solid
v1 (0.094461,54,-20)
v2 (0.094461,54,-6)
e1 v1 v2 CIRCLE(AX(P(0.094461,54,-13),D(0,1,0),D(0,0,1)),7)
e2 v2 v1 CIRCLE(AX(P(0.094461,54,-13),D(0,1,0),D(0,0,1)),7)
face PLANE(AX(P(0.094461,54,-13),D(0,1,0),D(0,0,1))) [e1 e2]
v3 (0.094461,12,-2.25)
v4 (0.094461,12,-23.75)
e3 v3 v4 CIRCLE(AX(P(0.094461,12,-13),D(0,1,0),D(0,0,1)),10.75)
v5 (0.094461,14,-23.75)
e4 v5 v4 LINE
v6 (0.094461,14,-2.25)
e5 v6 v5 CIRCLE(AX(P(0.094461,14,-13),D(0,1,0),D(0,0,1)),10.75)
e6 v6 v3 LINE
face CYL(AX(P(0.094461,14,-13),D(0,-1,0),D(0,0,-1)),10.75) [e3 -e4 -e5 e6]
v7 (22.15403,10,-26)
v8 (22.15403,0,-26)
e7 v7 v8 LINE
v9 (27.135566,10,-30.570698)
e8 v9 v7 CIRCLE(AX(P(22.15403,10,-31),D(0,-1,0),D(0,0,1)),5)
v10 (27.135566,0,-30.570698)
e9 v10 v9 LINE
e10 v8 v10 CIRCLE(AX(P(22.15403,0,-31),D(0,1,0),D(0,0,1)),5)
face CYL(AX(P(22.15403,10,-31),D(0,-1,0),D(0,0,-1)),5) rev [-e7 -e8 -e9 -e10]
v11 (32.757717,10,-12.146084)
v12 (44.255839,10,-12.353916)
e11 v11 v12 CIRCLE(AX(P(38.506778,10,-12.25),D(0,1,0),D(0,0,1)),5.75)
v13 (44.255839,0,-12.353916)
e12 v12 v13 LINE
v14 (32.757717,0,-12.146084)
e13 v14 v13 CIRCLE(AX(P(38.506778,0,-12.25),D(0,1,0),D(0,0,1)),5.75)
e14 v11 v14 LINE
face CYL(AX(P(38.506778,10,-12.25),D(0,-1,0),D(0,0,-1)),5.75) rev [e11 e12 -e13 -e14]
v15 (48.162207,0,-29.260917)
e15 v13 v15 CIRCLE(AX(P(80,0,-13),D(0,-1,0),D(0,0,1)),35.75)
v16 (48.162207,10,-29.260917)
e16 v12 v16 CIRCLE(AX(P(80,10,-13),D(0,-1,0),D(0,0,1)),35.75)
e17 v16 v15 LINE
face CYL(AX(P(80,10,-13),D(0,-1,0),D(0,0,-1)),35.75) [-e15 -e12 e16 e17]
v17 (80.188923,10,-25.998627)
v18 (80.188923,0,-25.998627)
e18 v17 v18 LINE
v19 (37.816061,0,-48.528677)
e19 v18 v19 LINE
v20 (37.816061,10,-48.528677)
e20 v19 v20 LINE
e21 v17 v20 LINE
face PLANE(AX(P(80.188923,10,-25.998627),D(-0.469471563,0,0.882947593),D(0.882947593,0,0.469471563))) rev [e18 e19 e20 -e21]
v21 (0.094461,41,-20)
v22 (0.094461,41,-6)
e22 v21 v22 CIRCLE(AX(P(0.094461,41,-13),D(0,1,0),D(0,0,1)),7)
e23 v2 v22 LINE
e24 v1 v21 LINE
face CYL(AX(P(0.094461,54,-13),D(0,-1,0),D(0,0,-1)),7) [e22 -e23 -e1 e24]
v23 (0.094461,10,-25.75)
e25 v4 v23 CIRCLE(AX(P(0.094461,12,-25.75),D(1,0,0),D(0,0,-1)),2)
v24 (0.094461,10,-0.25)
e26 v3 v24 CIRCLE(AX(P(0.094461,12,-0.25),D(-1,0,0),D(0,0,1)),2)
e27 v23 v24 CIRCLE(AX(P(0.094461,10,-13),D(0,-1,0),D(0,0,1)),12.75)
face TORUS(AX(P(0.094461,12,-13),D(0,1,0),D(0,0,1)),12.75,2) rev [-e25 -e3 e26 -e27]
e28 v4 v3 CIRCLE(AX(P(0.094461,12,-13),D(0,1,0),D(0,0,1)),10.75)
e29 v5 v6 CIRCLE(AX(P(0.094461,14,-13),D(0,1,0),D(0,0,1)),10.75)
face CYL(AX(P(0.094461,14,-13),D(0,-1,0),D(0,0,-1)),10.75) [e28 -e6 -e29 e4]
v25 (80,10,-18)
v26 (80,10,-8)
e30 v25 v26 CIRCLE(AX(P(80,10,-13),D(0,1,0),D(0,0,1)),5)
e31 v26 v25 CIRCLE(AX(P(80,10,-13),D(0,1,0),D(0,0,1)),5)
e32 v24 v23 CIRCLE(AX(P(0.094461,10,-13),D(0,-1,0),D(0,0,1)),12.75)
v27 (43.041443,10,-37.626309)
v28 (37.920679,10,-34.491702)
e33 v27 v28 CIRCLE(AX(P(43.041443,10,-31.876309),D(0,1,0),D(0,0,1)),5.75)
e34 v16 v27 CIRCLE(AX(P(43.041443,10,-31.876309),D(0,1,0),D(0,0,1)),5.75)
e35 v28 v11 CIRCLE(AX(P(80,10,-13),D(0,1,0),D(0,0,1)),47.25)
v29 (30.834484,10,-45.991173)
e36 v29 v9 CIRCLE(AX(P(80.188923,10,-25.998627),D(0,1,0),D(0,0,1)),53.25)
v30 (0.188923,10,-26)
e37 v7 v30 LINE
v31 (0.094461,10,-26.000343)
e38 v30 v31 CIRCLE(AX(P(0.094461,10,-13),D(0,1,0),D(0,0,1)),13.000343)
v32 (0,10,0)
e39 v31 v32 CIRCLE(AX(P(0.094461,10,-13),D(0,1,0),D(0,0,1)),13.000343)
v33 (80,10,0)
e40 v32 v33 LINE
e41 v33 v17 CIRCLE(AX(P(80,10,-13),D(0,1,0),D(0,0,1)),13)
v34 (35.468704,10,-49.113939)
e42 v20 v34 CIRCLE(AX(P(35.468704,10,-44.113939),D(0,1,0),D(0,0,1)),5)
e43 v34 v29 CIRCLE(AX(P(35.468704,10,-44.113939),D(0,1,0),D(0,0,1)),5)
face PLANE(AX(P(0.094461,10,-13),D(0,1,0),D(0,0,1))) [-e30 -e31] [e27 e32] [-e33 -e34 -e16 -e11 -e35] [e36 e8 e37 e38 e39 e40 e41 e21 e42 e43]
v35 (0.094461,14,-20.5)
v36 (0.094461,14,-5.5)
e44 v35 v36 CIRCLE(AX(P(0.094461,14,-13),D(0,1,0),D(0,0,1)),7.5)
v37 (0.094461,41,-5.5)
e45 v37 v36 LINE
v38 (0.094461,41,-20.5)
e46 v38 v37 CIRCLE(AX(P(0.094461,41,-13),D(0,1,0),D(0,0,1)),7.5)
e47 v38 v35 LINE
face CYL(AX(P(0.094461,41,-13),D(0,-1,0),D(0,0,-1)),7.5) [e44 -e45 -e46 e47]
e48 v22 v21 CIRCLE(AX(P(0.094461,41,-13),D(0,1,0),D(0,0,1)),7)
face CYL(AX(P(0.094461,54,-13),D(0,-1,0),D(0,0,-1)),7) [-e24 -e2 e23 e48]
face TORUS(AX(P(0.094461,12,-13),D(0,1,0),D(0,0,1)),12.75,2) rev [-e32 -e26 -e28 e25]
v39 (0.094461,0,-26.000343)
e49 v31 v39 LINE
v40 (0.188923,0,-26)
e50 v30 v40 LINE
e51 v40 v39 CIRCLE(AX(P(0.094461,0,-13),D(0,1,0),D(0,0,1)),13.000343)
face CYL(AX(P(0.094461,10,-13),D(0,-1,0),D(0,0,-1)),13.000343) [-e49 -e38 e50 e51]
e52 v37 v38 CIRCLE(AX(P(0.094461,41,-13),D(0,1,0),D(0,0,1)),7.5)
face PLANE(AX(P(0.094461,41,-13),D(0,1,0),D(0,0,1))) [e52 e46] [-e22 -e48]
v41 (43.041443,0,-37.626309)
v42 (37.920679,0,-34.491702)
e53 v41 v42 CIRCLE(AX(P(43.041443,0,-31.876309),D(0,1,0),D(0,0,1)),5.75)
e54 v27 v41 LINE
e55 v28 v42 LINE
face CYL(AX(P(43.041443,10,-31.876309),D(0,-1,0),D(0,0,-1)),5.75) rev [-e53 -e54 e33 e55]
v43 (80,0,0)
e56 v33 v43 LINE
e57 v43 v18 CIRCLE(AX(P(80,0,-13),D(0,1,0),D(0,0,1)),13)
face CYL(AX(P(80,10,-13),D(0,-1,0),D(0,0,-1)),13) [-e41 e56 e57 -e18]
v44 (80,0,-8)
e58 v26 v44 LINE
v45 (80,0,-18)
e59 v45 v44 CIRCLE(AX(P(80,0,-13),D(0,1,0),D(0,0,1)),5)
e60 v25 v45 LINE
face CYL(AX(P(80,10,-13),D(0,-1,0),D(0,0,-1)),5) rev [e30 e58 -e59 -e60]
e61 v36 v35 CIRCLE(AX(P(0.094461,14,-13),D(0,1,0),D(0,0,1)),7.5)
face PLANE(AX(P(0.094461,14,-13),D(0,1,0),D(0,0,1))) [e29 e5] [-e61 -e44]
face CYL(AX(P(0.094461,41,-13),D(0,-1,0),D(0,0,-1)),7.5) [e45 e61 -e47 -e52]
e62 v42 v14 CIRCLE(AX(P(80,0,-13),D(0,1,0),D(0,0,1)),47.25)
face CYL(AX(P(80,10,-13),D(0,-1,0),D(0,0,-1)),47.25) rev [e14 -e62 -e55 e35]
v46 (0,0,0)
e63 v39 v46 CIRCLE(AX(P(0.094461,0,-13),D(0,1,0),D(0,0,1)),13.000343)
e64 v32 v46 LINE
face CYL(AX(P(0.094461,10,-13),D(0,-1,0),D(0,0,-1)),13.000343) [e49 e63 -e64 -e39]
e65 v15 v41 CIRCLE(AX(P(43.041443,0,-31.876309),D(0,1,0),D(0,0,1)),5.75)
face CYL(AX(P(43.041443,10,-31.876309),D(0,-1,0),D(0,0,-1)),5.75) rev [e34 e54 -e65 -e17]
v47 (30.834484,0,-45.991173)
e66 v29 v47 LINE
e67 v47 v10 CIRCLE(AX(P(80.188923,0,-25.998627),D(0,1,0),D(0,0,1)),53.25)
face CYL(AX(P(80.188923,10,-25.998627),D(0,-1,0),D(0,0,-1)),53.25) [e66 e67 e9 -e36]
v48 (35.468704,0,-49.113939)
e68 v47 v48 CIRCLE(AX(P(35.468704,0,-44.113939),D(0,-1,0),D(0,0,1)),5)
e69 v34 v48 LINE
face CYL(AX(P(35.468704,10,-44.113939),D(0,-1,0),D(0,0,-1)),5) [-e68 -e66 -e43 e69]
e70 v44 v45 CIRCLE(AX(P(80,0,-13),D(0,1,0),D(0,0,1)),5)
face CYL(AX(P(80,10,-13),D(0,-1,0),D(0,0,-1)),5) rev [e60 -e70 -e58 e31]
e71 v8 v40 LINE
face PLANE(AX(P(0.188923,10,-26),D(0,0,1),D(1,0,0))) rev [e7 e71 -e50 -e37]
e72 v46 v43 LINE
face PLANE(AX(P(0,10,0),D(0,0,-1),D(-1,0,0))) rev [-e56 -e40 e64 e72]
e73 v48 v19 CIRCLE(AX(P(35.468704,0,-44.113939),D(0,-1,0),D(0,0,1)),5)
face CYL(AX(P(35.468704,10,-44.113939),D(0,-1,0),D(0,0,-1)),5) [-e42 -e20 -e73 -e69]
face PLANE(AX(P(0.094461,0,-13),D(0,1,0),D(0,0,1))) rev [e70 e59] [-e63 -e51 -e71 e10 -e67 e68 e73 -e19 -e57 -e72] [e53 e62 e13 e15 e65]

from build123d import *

# Parameters (mm, degrees)
SKETCH_1_R      = 5
EXTRUDE_1_DEPTH = 10
FILLET_2_R      = 5
SKETCH_2_R      = 10.75
EXTRUDE_2_DEPTH = 4
FILLET_3_R      = 2
SKETCH_3_R      = 7.5
EXTRUDE_3_DEPTH = 27
SKETCH_5_R      = 7
EXTRUDE_4_DEPTH = 13


with BuildPart() as part:
    # 草图1 → 凸台-拉伸1 (new body)
    with BuildSketch(Plane(origin=(0, 0, 0), x_dir=(1, 0, 0), z_dir=(0, 1, 0))):
        with BuildLine():
            Line((0, 0), (80, 0))
            ThreePointArc((80, 0), (92.999656788, 12.905536238), (80.188922536, 25.998627169))
            Line((80.188922536, 25.998627169), (33.171963216, 50.997987887))
            ThreePointArc((33.171963216, 50.997987887), (28.520841175, 38.881634135), (26.938922553, 26))
            Line((26.938922553, 26), (0.188922547, 26))
            ThreePointArc((0.188922547, 26), (-12.905538726, 13.094461274), (0, 0))
        make_face()
        with Locations(Location((80, 13, 0), (0, 0, 270))):
            Circle(SKETCH_1_R, mode=Mode.SUBTRACT)
        with BuildLine():
            ThreePointArc((48.162206807, 29.260917091), (45.167661271, 21.048023276), (44.255838588, 12.353915663))
            ThreePointArc((44.255838588, 12.353915663), (38.610693325, 6.500939074), (32.757716736, 12.146084337))
            ThreePointArc((32.757716736, 12.146084337), (33.962853008, 23.636897896), (37.920678927, 34.491701609))
            ThreePointArc((37.920678927, 34.491701609), (45.656835127, 36.99707329), (48.162206807, 29.260917091))
        make_face(mode=Mode.SUBTRACT)
    extrude(amount=EXTRUDE_1_DEPTH)

    # 圆角2
    fillet_2_edges = [part.edges().sort_by_distance(p)[0] for p in [
        (26.938922553, 5, -26),
        (33.171963216, 5, -50.997987887),
    ]]
    fillet(fillet_2_edges, radius=FILLET_2_R)

    # 草图2 → 凸台-拉伸2 (add)
    with BuildSketch(Plane(origin=(0, 10, 0), x_dir=(1, 0, 0), z_dir=(0, 1, 0))):
        with Locations(Location((0.094461274, 13, 0), (0, 0, 270))):
            Circle(SKETCH_2_R)
    extrude(amount=EXTRUDE_2_DEPTH)

    # 圆角3
    fillet_3_edges = [part.edges().sort_by_distance(p)[0] for p in [
        (0.094461274, 10, -23.75),
    ]]
    fillet(fillet_3_edges, radius=FILLET_3_R)

    # 草图3 → 凸台-拉伸3 (add)
    with BuildSketch(Plane(origin=(0, 14, 0), x_dir=(1, 0, 0), z_dir=(0, 1, 0))):
        with Locations(Location((0.094461274, 13, 0), (0, 0, 270))):
            Circle(SKETCH_3_R)
    extrude(amount=EXTRUDE_3_DEPTH)

    # 草图5 → 凸台-拉伸4 (add)
    with BuildSketch(Plane(origin=(0, 41, 0), x_dir=(1, 0, 0), z_dir=(0, 1, 0))):
        with Locations(Location((0.094461274, 13, 0), (0, 0, 90))):
            Circle(SKETCH_5_R)
    extrude(amount=EXTRUDE_4_DEPTH)


solid = part.part
